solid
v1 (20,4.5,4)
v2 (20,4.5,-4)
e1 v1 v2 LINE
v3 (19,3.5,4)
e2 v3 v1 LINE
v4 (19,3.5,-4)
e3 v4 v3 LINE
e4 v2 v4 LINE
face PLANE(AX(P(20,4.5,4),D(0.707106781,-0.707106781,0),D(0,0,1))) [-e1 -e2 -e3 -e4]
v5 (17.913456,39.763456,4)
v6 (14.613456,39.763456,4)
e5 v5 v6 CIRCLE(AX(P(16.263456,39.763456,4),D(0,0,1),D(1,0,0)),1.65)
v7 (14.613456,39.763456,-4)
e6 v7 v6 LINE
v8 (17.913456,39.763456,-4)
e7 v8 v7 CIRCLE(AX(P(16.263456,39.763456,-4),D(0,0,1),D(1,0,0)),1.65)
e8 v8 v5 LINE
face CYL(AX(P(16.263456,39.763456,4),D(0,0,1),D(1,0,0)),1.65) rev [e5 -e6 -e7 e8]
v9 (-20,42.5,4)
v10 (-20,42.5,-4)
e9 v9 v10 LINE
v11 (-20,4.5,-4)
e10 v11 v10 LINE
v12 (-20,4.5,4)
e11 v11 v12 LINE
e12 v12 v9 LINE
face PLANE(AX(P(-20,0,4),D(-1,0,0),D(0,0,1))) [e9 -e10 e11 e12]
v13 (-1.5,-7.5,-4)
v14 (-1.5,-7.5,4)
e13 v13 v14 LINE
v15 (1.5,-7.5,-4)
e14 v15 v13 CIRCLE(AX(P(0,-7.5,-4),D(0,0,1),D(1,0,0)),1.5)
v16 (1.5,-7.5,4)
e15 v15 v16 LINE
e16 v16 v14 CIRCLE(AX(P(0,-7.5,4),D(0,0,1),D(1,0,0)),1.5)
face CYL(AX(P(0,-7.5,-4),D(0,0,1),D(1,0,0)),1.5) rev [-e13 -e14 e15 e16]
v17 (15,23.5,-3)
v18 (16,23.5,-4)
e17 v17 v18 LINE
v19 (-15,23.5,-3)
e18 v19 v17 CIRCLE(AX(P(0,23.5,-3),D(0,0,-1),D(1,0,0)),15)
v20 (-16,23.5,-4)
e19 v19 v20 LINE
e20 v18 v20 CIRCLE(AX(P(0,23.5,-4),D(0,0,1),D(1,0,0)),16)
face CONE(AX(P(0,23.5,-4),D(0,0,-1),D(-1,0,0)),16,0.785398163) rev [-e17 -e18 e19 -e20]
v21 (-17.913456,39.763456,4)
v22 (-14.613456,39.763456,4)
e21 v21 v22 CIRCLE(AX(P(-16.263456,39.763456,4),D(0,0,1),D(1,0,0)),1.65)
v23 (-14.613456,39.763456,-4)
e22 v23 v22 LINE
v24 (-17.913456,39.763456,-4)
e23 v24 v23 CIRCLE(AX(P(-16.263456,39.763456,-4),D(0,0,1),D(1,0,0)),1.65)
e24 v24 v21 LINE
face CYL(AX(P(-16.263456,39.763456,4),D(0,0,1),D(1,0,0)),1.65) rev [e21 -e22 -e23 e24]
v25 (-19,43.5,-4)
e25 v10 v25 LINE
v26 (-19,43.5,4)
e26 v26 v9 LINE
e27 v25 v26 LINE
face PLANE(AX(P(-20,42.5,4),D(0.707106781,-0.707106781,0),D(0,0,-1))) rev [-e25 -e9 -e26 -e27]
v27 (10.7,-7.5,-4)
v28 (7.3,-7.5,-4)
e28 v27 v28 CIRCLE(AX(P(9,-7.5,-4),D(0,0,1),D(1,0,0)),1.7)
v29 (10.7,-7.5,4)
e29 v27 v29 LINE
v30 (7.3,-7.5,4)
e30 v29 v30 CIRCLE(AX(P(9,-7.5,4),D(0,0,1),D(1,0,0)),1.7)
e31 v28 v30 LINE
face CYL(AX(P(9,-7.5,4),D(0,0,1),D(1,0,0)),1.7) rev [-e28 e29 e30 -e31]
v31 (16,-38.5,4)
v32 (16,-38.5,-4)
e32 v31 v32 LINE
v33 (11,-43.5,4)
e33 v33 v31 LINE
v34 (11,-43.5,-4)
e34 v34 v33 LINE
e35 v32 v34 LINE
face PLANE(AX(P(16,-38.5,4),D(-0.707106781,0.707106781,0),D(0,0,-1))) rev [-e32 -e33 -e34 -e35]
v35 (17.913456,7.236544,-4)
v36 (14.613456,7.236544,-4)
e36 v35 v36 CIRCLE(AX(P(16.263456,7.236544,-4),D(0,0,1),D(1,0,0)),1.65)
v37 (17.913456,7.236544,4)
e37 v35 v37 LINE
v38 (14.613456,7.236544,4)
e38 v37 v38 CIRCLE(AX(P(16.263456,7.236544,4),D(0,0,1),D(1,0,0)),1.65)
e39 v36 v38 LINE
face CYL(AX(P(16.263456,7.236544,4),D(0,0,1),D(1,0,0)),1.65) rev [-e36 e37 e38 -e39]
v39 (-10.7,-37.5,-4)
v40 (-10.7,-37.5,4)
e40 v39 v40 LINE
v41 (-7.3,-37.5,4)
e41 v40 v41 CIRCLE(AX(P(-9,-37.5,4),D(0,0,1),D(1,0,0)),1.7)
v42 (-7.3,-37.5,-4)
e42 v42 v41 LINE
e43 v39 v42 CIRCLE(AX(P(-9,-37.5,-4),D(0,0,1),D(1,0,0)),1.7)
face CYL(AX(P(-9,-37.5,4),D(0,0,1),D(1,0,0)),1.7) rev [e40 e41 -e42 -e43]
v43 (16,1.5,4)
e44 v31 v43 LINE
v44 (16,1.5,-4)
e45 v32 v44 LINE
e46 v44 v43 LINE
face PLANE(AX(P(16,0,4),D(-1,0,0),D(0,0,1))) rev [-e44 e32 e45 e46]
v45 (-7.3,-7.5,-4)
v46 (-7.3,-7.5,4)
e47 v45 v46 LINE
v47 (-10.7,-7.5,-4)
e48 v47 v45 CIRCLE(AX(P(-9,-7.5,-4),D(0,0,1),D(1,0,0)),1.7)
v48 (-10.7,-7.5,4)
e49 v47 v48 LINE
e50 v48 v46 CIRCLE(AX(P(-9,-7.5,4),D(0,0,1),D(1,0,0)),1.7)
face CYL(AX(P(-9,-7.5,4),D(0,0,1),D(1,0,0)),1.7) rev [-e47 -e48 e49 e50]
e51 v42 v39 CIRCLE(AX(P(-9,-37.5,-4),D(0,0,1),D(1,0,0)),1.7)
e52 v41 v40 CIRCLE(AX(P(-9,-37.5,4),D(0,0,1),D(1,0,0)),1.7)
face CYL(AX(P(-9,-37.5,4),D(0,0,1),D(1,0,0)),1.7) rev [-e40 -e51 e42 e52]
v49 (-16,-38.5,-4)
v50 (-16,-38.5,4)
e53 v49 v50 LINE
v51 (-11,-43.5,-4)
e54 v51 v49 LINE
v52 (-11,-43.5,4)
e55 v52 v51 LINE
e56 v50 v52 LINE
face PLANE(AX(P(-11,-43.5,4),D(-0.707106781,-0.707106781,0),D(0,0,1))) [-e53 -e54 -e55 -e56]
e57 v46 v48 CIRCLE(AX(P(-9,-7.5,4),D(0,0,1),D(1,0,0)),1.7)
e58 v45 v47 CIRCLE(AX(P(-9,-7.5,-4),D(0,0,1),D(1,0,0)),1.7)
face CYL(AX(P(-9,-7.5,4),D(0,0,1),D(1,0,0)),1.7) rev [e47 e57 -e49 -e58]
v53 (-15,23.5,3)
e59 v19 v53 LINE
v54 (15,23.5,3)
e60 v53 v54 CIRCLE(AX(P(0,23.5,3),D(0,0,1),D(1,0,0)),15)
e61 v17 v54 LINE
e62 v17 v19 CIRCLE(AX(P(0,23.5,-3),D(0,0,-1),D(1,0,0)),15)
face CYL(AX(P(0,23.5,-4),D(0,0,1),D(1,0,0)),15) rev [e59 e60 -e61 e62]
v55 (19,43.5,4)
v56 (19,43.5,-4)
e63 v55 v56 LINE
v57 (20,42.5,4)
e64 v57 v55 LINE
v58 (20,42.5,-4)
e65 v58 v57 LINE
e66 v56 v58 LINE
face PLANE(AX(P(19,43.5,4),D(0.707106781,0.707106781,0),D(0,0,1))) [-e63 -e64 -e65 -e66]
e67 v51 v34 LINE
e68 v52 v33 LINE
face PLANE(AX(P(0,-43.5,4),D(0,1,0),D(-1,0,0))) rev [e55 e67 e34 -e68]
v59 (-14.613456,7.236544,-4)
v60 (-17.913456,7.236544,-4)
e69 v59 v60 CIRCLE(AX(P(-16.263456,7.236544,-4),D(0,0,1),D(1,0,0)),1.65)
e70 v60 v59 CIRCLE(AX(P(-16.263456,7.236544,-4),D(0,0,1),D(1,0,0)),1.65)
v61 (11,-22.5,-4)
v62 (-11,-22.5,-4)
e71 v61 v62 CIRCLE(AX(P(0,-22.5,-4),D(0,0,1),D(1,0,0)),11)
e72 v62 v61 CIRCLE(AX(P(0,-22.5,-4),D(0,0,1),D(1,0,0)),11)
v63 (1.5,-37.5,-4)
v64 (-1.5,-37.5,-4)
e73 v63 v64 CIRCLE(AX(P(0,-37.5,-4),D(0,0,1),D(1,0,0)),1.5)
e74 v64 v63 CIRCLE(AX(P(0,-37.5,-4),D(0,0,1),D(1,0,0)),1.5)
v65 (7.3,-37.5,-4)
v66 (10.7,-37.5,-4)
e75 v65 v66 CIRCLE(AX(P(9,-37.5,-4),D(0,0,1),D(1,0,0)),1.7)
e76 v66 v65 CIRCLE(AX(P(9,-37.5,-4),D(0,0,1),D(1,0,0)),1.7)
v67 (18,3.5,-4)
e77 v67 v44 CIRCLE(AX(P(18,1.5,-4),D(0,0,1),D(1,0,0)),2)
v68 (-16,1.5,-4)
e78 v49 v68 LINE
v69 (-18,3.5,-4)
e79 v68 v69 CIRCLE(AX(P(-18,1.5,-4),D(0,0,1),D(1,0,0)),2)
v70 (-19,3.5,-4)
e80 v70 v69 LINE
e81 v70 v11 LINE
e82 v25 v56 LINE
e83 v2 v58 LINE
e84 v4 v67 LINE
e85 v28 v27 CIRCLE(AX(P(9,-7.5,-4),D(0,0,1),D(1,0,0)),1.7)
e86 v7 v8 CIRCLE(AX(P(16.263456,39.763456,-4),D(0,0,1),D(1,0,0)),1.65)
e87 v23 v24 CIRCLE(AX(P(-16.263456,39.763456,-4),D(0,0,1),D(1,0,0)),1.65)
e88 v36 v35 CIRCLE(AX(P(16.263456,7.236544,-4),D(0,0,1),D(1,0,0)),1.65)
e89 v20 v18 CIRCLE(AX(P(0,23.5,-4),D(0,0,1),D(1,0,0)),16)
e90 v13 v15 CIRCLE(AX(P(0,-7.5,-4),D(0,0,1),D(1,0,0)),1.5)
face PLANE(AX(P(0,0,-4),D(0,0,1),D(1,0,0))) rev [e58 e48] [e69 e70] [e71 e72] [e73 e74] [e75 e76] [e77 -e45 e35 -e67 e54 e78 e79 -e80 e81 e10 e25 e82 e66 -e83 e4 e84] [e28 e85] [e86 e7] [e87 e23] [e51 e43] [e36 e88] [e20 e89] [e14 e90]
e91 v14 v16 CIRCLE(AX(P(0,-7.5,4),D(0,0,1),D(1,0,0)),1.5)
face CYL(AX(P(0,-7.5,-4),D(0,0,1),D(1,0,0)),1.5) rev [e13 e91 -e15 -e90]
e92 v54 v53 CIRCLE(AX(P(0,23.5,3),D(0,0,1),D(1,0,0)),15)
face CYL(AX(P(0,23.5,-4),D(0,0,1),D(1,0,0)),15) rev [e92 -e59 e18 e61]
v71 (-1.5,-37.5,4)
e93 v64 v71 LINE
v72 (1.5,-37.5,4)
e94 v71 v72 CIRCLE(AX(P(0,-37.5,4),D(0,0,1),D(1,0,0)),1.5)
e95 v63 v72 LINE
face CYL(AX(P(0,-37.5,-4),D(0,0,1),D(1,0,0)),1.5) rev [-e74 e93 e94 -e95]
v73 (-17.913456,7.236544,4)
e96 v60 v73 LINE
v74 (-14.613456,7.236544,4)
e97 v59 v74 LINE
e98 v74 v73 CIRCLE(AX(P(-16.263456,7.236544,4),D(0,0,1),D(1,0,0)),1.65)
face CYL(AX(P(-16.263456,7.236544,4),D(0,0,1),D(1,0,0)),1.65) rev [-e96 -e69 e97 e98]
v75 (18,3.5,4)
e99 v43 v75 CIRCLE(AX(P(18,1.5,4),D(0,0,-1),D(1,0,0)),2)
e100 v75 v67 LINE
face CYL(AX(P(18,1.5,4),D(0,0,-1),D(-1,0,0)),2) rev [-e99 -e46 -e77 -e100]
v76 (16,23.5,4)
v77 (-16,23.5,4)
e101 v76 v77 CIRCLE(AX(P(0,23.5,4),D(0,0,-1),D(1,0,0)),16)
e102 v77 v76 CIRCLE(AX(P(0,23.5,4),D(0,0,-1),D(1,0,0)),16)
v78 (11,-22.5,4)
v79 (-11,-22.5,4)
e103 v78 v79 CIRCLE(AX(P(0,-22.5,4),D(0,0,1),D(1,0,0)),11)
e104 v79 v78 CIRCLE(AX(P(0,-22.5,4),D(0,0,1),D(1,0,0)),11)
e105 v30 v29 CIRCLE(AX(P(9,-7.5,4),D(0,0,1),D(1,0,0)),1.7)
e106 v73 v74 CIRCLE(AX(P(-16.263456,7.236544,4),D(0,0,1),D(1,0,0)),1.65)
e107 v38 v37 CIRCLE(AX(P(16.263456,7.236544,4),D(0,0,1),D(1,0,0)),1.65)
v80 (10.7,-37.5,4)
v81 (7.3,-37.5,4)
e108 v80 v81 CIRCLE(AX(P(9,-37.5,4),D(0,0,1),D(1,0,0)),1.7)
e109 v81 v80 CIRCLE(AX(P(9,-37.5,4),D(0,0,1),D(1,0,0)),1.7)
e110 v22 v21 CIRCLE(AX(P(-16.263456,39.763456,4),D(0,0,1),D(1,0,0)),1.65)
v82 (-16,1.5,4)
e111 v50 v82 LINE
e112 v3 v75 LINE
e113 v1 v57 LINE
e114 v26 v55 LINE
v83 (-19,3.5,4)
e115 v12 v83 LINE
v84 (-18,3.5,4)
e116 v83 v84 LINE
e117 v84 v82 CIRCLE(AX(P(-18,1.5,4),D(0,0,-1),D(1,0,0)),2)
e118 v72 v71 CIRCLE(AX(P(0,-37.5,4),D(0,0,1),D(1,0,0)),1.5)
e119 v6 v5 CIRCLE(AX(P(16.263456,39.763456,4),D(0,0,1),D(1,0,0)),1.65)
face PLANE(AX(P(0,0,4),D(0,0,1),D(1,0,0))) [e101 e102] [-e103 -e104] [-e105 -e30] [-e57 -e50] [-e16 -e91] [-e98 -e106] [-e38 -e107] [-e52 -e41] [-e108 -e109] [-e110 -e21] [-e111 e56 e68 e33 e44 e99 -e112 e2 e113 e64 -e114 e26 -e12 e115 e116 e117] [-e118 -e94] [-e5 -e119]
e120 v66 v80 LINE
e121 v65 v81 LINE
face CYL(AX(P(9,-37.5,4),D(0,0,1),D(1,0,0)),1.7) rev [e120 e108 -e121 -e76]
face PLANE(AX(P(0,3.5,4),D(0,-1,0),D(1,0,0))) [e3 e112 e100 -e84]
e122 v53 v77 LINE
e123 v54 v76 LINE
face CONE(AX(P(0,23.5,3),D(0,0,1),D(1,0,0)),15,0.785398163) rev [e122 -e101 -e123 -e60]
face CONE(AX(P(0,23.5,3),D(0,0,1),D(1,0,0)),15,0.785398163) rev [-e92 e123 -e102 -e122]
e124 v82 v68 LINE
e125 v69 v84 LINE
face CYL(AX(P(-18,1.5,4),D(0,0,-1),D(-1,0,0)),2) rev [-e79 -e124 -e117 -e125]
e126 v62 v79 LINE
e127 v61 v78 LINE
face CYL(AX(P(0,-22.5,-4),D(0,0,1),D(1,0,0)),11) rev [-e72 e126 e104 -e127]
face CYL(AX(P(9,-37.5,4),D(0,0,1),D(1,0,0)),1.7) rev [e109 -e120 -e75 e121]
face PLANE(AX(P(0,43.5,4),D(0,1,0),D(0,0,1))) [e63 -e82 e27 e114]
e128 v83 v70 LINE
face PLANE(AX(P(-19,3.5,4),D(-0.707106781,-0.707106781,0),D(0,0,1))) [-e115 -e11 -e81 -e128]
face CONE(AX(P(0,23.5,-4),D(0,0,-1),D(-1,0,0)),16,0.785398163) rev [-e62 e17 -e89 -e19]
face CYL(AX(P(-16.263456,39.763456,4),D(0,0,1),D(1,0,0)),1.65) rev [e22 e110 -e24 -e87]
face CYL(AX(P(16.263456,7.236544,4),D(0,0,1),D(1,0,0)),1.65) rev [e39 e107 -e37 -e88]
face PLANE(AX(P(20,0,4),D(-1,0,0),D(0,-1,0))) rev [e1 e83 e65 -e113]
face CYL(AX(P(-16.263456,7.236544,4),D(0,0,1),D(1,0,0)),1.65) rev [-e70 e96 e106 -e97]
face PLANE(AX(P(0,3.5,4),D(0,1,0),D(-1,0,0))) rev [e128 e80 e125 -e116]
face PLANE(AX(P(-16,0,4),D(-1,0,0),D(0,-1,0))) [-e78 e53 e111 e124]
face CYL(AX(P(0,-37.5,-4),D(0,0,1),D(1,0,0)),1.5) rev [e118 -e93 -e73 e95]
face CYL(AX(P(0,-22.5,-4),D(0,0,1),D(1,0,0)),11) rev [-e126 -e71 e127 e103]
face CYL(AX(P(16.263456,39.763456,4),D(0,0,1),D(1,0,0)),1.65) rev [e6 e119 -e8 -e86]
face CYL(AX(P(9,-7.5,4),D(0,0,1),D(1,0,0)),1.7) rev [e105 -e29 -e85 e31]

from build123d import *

# Parameters (mm, degrees)
BOSS_EXTRUDE1_DEPTH  = 4
M4_TAPPED_HOLE1_D    = 3.3
M3_CLEARANCE_HOLE1_D = 3.4
SKETCH6_R            = 15
SKETCH6_R_2          = 1.5
SKETCH6_R_3          = 11
CUT_EXTRUDE1_DEPTH   = 49.541219597
CHAMFER1_SIZE        = 5
CHAMFER2_SIZE        = 1
FILLET1_R            = 2


with BuildPart() as part:
    # Sketch1 → Boss-Extrude1 (new, symmetric)
    with BuildSketch(Plane.XY):
        Polygon((-16, 3.5), (-16, -43.5), (16, -43.5), (16, 3.5), (20, 3.5), (20, 43.5), (-20, 43.5), (-20, 3.5), align=None)
    extrude(amount=BOSS_EXTRUDE1_DEPTH, both=True)

    # M4 Tapped Hole1 (through all)
    with Locations(Plane.XY.offset(4)):
        with Locations((-16.263455967, 39.763455967), (16.263455967, 39.763455967), (16.263455967, 7.236544033), (-16.263455967, 7.236544033)):
            Hole(M4_TAPPED_HOLE1_D / 2)

    # M3 Clearance Hole1 (through all)
    with Locations(Plane.XY.offset(4)):
        with Locations((-9, -7.5), (9, -7.5), (9, -37.5), (-9, -37.5)):
            Hole(M3_CLEARANCE_HOLE1_D / 2)

    # Sketch6 → Cut-Extrude1 (cut, through all)
    with BuildSketch(Plane.XY.offset(4)):
        with Locations((0, 23.5)):
            Circle(SKETCH6_R)
        with Locations((0, -7.5)):
            Circle(SKETCH6_R_2)
        with Locations((0, -37.5)):
            Circle(SKETCH6_R_2)
        with Locations((0, -22.5)):
            Circle(SKETCH6_R_3)
    extrude(amount=-CUT_EXTRUDE1_DEPTH, mode=Mode.SUBTRACT)

    # Chamfer1
    chamfer1_edges = [part.edges().sort_by_distance(p)[0] for p in [
        (16, -43.5, 0),
        (-16, -43.5, 0),
    ]]
    chamfer(chamfer1_edges, length=CHAMFER1_SIZE)

    # Chamfer2
    chamfer2_edges = [part.edges().sort_by_distance(p)[0] for p in [
        (-20, 3.5, 0),
        (-20, 43.5, 0),
        (20, 43.5, 0),
        (20, 3.5, 0),
        (-15, 23.5, -4),
        (-15, 23.5, 4),
    ]]
    chamfer(chamfer2_edges, length=CHAMFER2_SIZE)

    # Fillet1
    fillet1_edges = [part.edges().sort_by_distance(p)[0] for p in [
        (-16, 3.5, 0),
        (16, 3.5, 0),
    ]]
    fillet(fillet1_edges, radius=FILLET1_R)


solid = part.part
